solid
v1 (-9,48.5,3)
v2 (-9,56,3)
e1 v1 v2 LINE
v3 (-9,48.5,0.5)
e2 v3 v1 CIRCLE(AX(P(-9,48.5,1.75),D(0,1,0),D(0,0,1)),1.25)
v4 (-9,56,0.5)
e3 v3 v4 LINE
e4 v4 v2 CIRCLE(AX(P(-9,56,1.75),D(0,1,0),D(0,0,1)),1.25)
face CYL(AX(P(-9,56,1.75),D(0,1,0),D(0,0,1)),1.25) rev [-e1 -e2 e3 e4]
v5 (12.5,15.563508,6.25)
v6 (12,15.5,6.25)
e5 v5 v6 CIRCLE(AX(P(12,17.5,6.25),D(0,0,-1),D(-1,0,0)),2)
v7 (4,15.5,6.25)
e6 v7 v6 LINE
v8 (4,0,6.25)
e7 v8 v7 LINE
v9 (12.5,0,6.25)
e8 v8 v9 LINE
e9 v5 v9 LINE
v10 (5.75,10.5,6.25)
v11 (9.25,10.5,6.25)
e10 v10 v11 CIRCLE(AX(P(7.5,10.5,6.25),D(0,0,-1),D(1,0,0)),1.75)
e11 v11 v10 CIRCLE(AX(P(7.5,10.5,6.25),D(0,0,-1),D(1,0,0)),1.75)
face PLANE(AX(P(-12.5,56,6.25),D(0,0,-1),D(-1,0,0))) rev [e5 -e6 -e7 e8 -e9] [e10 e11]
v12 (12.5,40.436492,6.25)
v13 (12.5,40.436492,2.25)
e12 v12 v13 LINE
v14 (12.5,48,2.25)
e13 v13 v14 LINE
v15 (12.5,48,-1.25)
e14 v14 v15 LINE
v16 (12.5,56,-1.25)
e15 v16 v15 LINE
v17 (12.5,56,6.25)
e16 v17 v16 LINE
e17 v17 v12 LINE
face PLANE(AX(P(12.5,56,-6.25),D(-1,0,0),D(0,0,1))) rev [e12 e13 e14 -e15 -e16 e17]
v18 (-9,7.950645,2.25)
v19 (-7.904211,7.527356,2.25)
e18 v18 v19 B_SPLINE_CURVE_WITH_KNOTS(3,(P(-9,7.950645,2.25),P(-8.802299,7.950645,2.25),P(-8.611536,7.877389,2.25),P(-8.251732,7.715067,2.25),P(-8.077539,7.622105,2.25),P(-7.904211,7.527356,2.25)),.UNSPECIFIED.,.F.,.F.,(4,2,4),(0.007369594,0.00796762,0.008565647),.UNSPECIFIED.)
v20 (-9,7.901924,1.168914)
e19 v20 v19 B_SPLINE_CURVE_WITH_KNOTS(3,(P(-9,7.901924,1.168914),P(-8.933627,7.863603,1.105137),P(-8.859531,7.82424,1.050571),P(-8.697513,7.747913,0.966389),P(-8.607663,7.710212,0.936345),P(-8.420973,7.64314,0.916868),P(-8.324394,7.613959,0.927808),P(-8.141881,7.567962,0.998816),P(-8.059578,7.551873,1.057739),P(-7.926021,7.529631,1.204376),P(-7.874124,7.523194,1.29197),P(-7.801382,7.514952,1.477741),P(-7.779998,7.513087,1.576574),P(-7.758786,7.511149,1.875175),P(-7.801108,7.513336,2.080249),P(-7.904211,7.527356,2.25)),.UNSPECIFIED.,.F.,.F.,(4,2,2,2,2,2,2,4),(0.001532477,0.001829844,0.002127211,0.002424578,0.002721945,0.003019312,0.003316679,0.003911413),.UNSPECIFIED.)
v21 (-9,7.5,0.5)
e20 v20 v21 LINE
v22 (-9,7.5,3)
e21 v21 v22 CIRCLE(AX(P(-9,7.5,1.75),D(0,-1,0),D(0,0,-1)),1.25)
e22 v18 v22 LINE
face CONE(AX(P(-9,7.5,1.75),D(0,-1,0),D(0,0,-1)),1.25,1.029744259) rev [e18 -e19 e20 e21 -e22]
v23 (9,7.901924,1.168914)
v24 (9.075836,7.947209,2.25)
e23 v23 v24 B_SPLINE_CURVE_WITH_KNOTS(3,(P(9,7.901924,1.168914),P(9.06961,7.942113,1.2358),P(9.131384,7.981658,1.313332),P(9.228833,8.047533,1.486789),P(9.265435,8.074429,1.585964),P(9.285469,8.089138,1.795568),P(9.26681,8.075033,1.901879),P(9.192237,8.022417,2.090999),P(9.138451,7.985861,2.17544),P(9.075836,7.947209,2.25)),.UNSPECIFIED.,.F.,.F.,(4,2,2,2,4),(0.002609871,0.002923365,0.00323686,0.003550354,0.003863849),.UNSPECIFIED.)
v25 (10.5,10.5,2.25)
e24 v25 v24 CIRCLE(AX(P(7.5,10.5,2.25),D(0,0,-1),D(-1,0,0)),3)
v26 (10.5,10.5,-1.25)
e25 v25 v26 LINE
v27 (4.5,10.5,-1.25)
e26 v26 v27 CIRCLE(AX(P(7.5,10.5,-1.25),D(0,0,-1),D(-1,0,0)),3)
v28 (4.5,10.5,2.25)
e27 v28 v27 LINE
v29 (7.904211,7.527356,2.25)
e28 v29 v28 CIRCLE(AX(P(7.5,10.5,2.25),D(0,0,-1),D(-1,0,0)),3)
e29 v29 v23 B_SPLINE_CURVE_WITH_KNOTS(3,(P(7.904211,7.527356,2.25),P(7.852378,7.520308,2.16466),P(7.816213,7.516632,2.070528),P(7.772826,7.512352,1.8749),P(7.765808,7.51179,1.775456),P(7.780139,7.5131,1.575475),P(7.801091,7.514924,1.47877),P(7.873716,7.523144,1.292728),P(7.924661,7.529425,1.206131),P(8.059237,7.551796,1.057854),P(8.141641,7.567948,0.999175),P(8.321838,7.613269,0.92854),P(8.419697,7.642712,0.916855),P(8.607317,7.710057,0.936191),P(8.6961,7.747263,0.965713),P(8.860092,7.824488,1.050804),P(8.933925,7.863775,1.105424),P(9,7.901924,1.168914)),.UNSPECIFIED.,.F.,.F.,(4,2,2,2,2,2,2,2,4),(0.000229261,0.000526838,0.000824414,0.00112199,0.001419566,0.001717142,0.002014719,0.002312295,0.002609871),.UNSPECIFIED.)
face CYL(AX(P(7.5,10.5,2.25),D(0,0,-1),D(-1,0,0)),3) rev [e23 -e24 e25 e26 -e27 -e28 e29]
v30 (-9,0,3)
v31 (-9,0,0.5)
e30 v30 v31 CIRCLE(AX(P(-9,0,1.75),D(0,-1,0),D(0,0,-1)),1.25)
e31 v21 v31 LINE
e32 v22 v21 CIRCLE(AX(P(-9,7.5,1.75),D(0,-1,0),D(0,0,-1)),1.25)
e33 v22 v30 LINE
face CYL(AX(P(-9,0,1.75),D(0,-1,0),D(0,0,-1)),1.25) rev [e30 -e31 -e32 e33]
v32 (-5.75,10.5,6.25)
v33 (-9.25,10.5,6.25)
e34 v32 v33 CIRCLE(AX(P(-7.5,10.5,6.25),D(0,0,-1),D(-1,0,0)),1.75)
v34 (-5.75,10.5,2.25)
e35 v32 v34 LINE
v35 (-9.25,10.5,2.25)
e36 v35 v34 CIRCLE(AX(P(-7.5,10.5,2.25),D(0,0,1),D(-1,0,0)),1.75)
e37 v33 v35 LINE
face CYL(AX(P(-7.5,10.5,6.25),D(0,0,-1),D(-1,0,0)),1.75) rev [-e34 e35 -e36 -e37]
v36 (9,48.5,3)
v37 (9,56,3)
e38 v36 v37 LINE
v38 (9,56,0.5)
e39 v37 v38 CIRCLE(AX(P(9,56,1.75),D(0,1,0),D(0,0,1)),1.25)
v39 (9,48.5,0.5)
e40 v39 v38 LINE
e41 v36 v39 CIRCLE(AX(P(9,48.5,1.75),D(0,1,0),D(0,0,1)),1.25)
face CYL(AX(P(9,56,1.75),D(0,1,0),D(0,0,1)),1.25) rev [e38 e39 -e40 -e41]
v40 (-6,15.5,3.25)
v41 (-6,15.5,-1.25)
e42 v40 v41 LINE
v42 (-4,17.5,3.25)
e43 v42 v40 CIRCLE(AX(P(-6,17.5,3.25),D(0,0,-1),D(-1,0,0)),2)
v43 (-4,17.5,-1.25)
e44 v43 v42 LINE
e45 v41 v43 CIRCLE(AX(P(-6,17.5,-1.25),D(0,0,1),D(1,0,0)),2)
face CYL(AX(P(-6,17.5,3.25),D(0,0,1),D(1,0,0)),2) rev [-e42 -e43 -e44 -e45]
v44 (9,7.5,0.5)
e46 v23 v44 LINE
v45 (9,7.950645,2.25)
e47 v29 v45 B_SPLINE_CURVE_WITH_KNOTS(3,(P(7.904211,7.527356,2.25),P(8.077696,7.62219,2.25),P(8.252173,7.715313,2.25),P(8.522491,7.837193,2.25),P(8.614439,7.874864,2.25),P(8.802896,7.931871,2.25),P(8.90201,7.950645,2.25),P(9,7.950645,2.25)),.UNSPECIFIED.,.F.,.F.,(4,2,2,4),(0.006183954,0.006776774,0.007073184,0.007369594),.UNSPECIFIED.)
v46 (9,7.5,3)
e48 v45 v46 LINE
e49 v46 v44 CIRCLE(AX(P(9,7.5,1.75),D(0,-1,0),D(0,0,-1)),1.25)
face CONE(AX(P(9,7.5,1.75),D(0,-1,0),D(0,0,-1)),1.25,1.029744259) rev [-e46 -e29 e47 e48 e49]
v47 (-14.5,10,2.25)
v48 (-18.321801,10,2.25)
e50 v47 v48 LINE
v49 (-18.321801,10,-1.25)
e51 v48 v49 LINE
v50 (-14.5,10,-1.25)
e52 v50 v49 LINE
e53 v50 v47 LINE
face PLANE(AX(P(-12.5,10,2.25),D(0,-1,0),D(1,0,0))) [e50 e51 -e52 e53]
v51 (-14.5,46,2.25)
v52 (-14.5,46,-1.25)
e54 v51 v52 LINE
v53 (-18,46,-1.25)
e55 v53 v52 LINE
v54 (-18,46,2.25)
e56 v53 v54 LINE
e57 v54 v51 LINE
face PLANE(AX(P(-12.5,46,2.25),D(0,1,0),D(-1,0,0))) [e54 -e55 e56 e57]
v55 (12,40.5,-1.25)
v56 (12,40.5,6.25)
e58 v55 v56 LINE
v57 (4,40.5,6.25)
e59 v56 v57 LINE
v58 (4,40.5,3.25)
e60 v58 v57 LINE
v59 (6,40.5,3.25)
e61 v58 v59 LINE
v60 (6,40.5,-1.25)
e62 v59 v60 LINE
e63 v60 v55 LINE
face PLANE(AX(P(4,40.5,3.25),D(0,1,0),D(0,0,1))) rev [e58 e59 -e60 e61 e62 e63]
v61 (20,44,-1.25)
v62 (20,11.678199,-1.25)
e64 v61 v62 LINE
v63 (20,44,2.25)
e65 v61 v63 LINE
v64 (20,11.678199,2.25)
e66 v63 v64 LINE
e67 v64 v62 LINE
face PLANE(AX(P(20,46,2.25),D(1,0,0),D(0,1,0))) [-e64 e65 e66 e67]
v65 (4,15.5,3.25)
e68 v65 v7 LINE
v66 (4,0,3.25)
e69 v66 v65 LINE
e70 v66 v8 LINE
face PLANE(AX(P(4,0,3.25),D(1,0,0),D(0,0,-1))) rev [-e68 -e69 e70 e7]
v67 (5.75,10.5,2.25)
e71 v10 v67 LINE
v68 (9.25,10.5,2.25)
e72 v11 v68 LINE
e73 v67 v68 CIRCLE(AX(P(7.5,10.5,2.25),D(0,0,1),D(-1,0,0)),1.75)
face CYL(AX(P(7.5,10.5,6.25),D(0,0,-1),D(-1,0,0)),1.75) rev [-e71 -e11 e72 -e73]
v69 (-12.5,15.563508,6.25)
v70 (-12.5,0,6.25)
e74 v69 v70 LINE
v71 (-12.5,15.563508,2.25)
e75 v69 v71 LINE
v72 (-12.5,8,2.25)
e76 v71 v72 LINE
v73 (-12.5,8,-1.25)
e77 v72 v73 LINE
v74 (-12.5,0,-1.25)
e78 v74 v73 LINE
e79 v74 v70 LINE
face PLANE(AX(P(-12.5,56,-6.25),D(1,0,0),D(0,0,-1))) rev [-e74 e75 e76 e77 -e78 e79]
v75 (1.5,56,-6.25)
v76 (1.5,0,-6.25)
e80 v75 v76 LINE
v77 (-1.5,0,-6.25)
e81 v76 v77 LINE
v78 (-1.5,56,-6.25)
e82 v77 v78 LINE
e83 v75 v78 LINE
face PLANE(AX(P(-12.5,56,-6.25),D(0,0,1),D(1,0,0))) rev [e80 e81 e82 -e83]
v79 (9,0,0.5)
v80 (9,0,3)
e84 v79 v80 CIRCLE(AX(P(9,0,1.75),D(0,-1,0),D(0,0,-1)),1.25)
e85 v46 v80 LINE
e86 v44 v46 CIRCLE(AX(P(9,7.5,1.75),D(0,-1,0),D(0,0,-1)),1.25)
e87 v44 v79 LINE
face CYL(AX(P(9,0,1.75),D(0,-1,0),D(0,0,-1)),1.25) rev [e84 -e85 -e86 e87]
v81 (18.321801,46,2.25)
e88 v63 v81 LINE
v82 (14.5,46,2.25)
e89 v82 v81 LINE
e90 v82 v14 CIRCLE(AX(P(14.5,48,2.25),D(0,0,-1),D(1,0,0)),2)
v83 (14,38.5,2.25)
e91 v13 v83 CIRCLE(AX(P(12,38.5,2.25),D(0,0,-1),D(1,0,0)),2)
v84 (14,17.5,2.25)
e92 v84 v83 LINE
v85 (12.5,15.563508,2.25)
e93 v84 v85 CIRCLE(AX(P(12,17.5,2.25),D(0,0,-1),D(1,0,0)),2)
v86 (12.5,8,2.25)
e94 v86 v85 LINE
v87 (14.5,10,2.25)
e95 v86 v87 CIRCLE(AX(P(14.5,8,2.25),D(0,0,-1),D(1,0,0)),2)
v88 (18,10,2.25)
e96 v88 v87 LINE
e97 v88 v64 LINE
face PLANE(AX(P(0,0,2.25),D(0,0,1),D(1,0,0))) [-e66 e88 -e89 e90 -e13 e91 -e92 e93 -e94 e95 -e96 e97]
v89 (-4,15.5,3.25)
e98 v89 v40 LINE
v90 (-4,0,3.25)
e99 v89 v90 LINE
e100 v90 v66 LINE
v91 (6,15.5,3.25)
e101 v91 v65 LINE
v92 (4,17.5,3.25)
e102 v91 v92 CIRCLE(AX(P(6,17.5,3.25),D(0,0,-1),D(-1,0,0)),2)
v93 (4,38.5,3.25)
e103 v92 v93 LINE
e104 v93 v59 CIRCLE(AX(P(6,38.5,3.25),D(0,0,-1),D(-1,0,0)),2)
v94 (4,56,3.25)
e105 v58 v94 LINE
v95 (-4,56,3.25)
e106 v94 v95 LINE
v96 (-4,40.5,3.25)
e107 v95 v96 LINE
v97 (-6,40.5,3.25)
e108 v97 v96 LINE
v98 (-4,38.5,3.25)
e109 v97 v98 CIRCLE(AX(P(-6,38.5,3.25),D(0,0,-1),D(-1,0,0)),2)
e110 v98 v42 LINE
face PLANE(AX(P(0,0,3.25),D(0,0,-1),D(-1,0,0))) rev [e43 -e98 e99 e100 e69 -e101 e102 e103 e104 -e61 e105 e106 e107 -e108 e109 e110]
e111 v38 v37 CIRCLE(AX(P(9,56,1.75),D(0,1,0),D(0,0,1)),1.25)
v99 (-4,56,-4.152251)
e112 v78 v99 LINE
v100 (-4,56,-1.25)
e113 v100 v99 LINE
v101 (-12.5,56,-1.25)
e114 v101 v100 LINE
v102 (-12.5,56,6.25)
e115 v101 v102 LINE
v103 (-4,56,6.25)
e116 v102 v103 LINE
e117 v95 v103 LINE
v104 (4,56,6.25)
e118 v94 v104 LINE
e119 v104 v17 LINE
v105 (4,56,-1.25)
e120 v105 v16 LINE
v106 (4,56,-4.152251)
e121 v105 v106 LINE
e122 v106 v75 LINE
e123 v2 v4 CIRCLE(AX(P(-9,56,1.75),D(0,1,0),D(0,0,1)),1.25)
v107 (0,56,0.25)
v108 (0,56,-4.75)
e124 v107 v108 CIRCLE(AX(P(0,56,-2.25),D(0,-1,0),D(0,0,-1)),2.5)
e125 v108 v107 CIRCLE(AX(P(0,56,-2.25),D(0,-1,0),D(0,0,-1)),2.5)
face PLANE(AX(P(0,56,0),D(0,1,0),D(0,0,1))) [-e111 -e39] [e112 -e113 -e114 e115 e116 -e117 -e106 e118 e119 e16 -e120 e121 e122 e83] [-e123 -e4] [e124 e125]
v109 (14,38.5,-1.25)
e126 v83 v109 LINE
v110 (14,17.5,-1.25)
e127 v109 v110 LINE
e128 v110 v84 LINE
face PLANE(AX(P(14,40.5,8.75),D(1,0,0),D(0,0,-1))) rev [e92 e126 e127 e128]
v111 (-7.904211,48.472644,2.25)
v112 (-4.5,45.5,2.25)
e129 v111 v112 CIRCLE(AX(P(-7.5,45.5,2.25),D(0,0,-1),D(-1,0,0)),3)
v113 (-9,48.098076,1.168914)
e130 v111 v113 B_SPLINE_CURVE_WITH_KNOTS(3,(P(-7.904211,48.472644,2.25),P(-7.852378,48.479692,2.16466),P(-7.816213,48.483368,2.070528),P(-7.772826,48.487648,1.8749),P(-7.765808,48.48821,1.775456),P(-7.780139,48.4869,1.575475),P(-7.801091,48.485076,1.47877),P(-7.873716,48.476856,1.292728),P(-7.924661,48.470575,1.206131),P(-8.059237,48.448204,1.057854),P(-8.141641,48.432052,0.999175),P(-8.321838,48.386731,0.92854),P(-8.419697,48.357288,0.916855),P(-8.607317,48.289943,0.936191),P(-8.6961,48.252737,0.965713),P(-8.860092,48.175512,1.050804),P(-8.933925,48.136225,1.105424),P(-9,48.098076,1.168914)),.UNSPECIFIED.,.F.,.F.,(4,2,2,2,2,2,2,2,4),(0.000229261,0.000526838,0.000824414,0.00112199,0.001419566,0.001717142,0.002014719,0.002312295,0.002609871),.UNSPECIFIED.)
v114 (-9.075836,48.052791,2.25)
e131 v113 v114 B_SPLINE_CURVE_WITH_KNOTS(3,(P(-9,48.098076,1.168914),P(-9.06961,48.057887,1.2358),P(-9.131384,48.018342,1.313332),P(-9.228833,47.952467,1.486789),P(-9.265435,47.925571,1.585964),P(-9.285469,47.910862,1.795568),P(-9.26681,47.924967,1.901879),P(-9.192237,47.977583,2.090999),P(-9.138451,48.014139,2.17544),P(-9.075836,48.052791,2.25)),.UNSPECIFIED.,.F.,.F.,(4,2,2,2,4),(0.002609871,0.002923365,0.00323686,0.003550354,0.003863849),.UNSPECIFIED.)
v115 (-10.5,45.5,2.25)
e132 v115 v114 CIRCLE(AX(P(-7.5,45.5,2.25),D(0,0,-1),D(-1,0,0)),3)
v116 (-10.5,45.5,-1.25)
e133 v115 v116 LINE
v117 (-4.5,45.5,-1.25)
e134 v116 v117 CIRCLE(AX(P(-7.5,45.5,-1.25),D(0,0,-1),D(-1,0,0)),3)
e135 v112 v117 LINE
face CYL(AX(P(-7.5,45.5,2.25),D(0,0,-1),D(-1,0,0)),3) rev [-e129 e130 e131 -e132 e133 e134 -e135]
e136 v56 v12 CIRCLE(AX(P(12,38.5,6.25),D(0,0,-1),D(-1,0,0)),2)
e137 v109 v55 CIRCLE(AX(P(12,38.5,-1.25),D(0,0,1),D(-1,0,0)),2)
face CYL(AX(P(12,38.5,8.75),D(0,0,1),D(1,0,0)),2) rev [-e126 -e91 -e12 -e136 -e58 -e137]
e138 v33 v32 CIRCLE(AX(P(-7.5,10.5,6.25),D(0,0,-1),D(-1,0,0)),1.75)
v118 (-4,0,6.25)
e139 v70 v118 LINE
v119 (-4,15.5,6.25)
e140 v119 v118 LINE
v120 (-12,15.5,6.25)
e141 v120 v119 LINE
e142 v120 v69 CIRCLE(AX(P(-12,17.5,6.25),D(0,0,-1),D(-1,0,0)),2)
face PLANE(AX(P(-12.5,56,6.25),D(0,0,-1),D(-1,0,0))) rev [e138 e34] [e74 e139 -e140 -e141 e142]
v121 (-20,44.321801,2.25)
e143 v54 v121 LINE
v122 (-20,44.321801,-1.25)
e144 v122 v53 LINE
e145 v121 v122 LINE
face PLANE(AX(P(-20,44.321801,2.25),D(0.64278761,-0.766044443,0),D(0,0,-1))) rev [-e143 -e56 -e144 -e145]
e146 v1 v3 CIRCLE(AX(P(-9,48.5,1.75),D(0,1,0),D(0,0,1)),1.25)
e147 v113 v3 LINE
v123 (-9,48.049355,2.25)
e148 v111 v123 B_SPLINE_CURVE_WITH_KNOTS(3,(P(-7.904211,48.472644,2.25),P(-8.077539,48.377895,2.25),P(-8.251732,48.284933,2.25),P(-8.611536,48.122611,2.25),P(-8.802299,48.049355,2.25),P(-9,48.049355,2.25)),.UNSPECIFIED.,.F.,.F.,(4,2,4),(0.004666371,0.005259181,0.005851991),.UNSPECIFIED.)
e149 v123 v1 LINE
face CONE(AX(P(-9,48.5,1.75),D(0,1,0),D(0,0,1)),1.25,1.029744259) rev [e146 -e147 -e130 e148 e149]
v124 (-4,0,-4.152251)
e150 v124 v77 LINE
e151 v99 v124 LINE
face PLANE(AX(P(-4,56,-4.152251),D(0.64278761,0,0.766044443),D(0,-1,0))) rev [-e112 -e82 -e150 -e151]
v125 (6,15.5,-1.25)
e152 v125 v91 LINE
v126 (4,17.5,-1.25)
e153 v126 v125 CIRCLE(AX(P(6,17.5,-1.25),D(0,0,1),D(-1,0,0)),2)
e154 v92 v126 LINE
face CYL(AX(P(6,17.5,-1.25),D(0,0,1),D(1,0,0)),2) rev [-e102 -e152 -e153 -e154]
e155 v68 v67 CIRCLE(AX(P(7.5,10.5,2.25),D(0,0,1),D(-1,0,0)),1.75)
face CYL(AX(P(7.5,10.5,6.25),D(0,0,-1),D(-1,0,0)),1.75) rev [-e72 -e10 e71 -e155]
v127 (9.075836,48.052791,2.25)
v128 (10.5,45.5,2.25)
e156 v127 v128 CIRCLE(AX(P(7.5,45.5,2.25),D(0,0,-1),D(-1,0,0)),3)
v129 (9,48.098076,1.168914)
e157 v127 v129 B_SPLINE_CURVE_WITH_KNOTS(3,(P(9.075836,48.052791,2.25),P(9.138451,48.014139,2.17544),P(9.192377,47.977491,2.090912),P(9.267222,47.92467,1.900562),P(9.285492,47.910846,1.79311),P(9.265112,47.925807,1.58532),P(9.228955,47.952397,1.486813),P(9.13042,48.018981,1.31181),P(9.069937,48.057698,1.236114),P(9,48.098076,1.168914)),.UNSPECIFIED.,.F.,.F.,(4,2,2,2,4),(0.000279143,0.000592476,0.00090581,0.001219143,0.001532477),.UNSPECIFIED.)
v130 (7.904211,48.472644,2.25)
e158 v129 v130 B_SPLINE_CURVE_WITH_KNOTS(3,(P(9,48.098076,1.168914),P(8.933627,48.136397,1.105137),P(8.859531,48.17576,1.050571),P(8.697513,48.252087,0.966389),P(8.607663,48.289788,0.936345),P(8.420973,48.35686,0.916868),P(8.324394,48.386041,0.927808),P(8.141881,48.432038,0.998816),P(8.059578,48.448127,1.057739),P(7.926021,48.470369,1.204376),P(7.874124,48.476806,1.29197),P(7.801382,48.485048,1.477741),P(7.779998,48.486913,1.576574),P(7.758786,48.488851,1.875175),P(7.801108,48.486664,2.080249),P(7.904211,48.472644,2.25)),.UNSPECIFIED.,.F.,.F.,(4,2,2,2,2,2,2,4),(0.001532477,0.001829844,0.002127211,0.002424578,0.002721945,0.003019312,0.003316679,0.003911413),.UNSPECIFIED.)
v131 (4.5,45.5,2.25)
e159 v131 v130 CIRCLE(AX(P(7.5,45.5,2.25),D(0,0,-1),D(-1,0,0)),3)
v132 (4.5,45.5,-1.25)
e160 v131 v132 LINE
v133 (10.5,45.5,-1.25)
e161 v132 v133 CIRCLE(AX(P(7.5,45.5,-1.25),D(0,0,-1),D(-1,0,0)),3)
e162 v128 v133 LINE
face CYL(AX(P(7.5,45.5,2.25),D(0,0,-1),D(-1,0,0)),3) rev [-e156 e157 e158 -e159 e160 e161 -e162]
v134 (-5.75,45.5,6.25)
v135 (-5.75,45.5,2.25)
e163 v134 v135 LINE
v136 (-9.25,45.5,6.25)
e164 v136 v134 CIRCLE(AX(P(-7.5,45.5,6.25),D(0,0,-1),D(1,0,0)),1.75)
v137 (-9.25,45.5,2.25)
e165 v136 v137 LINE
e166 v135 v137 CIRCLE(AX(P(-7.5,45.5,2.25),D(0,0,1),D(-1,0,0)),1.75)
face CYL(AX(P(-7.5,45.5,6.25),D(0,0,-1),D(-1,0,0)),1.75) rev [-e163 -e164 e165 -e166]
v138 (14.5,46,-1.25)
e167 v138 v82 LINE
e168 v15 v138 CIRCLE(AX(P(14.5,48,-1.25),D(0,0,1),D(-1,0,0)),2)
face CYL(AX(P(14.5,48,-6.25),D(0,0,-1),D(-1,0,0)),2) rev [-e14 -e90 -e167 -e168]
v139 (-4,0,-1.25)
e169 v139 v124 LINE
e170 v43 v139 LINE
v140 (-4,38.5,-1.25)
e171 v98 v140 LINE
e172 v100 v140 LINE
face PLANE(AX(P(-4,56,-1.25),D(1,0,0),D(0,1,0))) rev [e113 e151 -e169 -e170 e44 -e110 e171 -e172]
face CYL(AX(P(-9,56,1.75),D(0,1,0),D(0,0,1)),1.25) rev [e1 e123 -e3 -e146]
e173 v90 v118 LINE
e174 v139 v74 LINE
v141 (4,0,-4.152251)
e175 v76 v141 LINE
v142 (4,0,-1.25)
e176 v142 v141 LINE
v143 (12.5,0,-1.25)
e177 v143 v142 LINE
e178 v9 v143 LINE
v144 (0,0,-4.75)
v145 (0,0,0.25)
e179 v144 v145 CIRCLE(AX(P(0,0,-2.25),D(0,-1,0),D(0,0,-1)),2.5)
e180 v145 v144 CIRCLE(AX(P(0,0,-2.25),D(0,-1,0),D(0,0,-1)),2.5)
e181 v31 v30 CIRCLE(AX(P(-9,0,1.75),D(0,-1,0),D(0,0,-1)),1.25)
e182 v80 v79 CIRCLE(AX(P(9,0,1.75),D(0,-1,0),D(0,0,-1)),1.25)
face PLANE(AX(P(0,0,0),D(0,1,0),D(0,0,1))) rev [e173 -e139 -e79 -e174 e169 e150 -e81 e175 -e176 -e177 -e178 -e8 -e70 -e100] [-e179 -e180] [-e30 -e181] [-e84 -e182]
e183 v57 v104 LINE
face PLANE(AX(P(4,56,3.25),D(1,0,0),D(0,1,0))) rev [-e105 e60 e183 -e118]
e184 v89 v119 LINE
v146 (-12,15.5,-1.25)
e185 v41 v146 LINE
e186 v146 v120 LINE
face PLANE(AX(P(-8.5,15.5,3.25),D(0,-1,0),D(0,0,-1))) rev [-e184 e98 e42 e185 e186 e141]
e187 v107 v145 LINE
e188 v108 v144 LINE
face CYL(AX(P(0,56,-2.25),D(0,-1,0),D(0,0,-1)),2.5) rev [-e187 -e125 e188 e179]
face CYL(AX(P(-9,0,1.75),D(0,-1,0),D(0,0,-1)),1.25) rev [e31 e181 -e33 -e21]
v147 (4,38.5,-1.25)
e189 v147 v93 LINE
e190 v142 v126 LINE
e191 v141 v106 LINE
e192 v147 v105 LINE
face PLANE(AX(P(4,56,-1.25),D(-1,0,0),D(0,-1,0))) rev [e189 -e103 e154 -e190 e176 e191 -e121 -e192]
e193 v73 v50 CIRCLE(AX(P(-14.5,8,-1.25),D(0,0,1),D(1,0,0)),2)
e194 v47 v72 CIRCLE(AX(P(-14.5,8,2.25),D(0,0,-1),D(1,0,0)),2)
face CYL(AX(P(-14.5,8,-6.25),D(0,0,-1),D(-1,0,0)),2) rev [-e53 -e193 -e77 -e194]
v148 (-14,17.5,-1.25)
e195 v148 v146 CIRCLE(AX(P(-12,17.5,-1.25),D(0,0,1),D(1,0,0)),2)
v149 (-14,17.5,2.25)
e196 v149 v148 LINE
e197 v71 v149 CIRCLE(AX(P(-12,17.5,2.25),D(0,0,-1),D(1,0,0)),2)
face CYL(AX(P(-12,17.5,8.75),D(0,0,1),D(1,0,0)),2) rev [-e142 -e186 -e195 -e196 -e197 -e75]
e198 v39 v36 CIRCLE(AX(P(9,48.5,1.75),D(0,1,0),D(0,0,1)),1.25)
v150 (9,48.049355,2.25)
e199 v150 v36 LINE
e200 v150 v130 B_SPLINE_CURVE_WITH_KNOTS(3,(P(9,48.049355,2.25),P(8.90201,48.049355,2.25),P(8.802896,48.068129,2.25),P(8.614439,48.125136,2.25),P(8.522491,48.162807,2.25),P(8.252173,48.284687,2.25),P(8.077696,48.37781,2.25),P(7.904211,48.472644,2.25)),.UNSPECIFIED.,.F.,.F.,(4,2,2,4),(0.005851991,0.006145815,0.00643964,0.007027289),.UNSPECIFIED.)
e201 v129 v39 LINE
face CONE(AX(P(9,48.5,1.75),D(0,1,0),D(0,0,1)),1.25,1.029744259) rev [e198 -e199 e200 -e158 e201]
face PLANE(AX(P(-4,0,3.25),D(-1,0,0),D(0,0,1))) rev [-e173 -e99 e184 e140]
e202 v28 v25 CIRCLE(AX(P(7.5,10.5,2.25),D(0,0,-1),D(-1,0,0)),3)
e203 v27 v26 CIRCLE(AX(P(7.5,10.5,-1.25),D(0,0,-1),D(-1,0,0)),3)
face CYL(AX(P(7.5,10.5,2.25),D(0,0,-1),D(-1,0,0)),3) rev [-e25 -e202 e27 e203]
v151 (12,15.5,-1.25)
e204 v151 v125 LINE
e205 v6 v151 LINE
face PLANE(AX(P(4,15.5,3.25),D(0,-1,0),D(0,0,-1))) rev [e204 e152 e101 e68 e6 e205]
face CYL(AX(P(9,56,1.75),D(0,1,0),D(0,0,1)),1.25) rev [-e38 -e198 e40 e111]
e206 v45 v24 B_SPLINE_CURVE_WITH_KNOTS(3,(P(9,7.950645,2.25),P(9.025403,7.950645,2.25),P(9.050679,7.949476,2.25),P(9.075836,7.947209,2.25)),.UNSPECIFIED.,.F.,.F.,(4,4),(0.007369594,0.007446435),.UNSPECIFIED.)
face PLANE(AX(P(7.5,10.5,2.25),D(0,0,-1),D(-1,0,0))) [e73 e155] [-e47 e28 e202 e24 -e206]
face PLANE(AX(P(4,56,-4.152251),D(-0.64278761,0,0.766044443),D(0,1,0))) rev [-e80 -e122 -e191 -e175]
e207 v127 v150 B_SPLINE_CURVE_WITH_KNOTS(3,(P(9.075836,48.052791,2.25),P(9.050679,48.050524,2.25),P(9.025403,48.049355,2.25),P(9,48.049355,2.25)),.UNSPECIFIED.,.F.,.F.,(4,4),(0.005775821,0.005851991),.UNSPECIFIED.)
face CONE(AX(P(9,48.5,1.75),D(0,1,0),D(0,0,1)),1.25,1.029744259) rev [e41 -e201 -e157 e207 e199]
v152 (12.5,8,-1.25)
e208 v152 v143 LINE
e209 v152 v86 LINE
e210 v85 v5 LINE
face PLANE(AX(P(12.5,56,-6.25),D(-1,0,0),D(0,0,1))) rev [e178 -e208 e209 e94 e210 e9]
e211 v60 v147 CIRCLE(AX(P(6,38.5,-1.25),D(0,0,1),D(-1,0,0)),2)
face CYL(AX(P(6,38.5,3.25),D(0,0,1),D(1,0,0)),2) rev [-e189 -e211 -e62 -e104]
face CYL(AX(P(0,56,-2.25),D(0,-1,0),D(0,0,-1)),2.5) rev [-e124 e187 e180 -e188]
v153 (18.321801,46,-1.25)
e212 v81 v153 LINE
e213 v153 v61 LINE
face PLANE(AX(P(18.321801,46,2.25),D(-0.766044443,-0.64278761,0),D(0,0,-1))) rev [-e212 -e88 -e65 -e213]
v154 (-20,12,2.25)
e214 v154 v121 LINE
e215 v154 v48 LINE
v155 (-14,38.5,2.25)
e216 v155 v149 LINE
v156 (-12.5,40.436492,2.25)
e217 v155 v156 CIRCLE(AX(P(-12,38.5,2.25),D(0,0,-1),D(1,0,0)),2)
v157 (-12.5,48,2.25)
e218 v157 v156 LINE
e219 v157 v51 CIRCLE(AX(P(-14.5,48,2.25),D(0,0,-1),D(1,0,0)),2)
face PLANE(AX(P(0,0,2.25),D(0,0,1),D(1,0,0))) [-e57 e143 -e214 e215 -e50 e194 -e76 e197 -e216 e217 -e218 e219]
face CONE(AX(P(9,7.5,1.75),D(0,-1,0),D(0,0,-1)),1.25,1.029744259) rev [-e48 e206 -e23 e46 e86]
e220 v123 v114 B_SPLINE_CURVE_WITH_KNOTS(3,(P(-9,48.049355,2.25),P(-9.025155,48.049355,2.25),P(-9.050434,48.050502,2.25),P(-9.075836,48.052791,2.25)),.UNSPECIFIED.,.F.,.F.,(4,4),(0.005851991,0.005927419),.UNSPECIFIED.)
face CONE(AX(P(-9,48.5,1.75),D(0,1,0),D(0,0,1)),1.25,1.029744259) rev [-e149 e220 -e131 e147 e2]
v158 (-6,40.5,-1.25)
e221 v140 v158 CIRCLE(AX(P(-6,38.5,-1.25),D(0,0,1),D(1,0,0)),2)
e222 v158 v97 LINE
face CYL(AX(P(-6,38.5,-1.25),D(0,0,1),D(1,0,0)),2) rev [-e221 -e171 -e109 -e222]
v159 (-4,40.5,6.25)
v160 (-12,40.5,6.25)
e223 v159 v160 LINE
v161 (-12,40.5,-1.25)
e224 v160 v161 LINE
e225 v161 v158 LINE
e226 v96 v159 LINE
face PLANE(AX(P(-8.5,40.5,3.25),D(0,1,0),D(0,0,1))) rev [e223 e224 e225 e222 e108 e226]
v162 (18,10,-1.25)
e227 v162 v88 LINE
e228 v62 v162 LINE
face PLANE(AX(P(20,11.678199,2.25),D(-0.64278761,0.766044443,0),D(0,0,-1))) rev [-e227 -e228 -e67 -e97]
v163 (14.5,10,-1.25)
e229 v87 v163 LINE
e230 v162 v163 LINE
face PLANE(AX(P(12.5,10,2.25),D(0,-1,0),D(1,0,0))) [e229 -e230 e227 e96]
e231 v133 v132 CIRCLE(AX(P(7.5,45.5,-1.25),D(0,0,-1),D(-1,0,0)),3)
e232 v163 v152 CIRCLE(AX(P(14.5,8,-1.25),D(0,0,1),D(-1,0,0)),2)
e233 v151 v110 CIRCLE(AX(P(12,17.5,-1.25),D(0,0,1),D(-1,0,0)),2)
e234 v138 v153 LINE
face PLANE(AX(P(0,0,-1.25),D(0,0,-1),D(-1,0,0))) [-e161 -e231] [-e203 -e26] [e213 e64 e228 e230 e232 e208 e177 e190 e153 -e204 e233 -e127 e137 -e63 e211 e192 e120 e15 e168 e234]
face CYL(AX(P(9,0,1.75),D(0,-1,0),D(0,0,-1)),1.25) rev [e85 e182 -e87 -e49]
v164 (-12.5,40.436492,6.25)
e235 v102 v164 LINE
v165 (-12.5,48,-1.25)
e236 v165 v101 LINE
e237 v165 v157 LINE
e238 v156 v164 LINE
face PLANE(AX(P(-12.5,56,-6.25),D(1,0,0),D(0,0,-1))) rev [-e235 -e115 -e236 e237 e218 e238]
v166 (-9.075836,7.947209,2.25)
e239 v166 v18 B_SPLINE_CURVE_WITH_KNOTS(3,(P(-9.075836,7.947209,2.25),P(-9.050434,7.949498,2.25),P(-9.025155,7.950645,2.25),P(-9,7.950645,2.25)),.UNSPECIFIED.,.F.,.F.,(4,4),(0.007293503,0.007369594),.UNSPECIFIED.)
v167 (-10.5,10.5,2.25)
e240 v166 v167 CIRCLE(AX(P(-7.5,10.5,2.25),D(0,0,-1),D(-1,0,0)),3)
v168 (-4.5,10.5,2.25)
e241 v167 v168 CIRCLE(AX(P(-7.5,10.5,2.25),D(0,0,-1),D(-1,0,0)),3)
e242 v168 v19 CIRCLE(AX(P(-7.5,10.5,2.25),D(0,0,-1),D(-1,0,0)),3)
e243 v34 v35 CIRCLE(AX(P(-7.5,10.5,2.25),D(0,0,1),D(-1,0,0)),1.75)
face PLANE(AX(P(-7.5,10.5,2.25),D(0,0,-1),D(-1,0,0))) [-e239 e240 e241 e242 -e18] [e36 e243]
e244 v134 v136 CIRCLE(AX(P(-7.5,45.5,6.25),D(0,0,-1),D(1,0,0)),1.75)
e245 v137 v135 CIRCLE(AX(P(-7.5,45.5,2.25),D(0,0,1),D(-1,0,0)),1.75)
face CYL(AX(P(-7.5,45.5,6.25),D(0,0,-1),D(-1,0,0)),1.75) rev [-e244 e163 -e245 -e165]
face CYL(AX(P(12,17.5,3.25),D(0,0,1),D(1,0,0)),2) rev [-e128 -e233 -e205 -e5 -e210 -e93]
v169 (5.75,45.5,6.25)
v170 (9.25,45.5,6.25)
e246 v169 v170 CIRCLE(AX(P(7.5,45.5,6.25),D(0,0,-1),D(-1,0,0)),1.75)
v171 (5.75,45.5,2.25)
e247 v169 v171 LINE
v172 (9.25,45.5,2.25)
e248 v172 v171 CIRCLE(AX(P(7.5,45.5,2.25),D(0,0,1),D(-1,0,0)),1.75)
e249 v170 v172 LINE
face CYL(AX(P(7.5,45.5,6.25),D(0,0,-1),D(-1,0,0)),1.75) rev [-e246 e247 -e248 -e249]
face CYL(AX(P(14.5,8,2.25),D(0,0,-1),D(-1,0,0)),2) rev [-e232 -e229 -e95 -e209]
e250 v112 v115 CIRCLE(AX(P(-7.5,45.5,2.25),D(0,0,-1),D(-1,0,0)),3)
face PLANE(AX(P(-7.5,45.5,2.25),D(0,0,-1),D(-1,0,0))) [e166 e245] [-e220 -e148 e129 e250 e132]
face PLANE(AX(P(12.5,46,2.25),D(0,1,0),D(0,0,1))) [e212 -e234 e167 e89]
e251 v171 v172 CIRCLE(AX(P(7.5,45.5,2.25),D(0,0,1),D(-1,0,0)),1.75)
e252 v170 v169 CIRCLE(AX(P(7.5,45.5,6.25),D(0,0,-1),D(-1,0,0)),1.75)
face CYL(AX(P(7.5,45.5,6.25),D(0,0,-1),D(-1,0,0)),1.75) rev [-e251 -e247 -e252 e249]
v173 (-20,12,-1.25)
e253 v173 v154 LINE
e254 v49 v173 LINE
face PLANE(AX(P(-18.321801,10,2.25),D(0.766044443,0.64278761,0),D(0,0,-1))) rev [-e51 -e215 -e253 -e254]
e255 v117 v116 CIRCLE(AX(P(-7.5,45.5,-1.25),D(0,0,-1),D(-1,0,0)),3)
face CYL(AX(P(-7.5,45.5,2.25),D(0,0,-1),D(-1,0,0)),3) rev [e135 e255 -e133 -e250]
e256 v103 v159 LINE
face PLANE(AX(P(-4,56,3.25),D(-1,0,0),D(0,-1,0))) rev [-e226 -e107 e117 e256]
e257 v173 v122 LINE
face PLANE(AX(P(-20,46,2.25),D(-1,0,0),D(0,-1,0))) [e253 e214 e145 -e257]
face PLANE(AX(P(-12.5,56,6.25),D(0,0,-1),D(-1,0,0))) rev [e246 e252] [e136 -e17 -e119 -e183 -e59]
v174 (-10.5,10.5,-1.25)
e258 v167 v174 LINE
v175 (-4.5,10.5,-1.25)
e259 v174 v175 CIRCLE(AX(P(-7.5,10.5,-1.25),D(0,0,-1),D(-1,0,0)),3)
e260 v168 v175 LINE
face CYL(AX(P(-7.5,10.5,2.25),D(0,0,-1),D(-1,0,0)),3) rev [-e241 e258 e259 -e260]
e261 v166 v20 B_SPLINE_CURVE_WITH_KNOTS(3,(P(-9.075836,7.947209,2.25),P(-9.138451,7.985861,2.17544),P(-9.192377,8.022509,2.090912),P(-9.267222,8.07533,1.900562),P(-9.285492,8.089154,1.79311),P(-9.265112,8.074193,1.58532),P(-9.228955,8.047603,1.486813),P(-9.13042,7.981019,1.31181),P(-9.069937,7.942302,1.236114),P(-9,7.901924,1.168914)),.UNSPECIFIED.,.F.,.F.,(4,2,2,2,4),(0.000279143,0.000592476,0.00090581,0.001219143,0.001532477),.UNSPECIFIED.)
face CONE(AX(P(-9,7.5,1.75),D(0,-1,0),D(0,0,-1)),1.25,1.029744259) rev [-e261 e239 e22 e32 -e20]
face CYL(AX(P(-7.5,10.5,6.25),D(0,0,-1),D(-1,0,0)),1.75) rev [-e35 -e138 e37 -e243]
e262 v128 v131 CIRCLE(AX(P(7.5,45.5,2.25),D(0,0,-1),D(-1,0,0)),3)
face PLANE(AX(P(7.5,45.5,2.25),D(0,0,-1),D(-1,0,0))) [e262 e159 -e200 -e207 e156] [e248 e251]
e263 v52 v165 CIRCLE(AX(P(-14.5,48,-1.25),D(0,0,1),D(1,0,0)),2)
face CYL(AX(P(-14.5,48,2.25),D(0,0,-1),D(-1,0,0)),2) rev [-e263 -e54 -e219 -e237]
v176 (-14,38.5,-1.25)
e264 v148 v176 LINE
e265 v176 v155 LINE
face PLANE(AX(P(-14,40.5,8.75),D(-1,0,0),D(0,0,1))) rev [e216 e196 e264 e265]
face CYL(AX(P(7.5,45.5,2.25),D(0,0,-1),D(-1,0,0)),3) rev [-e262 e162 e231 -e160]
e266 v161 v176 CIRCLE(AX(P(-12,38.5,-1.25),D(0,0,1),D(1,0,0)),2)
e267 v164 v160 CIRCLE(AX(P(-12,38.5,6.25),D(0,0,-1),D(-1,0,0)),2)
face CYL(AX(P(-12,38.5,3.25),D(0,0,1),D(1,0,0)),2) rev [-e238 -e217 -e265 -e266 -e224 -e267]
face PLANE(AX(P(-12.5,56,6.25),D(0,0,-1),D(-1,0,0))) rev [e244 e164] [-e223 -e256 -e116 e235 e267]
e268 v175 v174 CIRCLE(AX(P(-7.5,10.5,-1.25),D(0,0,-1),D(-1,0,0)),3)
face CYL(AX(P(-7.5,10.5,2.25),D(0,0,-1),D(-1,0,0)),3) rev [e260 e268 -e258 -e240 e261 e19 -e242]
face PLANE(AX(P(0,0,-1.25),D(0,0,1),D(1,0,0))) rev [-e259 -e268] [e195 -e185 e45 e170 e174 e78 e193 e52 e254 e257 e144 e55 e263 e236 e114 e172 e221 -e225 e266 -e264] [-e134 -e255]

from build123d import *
from OCP.BRepFilletAPI import BRepFilletAPI_MakeChamfer

# Parameters (mm, degrees)
SKETCH1_W             = 25
SKETCH1_H             = 12.5
BOSS_EXTRUDE1_DEPTH   = 56
SKETCH3_W             = 8.5
SKETCH3_H             = 56
CUT_EXTRUDE2_DEPTH    = 5
SKETCH4_R             = 2.5
CUT_EXTRUDE3_DEPTH    = 58.717523336
SKETCH5_R             = 1.75
CUT_EXTRUDE4_DEPTH    = 58.866225037
SKETCH6_R             = 3
CUT_EXTRUDE5_DEPTH    = 3.5
CHAMFER1_SIZE         = 2.5
CHAMFER1_SIZE2        = 2.097749078
SKETCH8_W             = 7.5
SKETCH8_H             = 36
BOSS_EXTRUDE3_DEPTH   = 3.5
M3_TAPPED_HOLE1_D     = 2.5
M3_TAPPED_HOLE1_DEPTH = 7.5
M3_TAPPED_HOLE1_TIP   = 0.751075774
M3_TAPPED_HOLE2_D     = 2.5
M3_TAPPED_HOLE2_DEPTH = 7.5
M3_TAPPED_HOLE2_TIP   = 0.751075774
CHAMFER2_SIZE         = 2
CHAMFER2_SIZE2        = 1.678199262
FILLET1_R             = 2
CUT_EXTRUDE7_DEPTH    = 3
SKETCH17_W            = 10
SKETCH17_H            = 25
CUT_EXTRUDE8_DEPTH    = 10
FILLET3_R             = 2


with BuildPart() as part:
    # Sketch1 → Boss-Extrude1 (new body)
    with BuildSketch(Plane(origin=(0, 0, 0), x_dir=(1, 0, 0), z_dir=(0, 1, 0))):
        Rectangle(SKETCH1_W, SKETCH1_H)
    extrude(amount=BOSS_EXTRUDE1_DEPTH)

    # Sketch3 → Cut-Extrude2 (cut)
    with BuildSketch(Plane(origin=(0, 0, -6.25), x_dir=(-1, 0, 0), z_dir=(0, 0, -1))):
        with Locations((-8.25, 28)):
            Rectangle(SKETCH3_W, SKETCH3_H)
        with Locations((8.25, 28)):
            Rectangle(SKETCH3_W, SKETCH3_H)
    extrude(amount=-CUT_EXTRUDE2_DEPTH, mode=Mode.SUBTRACT)

    # Sketch4 → Cut-Extrude3 (cut, through all)
    with BuildSketch(Plane.XZ):
        with Locations(Location((0, -2.25, 0), (0, 0, 270))):
            Circle(SKETCH4_R)
    extrude(amount=-CUT_EXTRUDE3_DEPTH, mode=Mode.SUBTRACT)

    # Sketch5 → Cut-Extrude4 (cut, through all)
    with BuildSketch(Plane(origin=(0, 0, -1.25), x_dir=(-1, 0, 0), z_dir=(0, 0, -1))):
        with Locations((-7.5, 45.5)):
            Circle(SKETCH5_R)
        with Locations((7.5, 45.5)):
            Circle(SKETCH5_R)
        with Locations((7.5, 10.5)):
            Circle(SKETCH5_R)
        with Locations((-7.5, 10.5)):
            Circle(SKETCH5_R)
    extrude(amount=-CUT_EXTRUDE4_DEPTH, mode=Mode.SUBTRACT)

    # Sketch6 → Cut-Extrude5 (cut)
    with BuildSketch(Plane(origin=(0, 0, -1.25), x_dir=(-1, 0, 0), z_dir=(0, 0, -1))):
        with Locations((-7.5, 45.5)):
            Circle(SKETCH6_R)
        with Locations((7.5, 45.5)):
            Circle(SKETCH6_R)
        with Locations((7.5, 10.5)):
            Circle(SKETCH6_R)
        with Locations((-7.5, 10.5)):
            Circle(SKETCH6_R)
    extrude(amount=-CUT_EXTRUDE5_DEPTH, mode=Mode.SUBTRACT)

    # Chamfer1
    chamfer1_edges = [part.edges().sort_by_distance(p)[0] for p in [
        (4, 28, -6.25),
        (-4, 28, -6.25),
    ]]
    chamfer1_side = [part.faces().sort_by_distance(p)[0] for p in [
        (0, 28, -6.25),
    ]]
    chamfer(chamfer1_edges, length=CHAMFER1_SIZE, length2=CHAMFER1_SIZE2, reference=chamfer1_side[0])

    # Sketch8 → Boss-Extrude3 (add)
    with BuildSketch(Plane(origin=(0, 0, -1.25), x_dir=(-1, 0, 0), z_dir=(0, 0, -1))):
        with Locations((-16.25, 28)):
            Rectangle(SKETCH8_W, SKETCH8_H)
        with Locations((16.25, 28)):
            Rectangle(SKETCH8_W, SKETCH8_H)
    extrude(amount=-BOSS_EXTRUDE3_DEPTH)

    # M3 Tapped Hole1
    with Locations(Plane(origin=(0, 0, 0), x_dir=(-1, 0, 0), z_dir=(0, -1, 0))):
        with Locations((-9, -1.75), (9, -1.75)):
            Hole(M3_TAPPED_HOLE1_D / 2, depth=M3_TAPPED_HOLE1_DEPTH)
            with Locations((0, 0, -(M3_TAPPED_HOLE1_DEPTH + M3_TAPPED_HOLE1_TIP / 2))):  # 118° drill point
                Cone(0, M3_TAPPED_HOLE1_D / 2, M3_TAPPED_HOLE1_TIP, mode=Mode.SUBTRACT)

    # M3 Tapped Hole2
    with Locations(Plane(origin=(0, 56, 0), x_dir=(1, 0, 0), z_dir=(0, 1, 0))):
        with Locations((-9, -1.75), (9, -1.75)):
            Hole(M3_TAPPED_HOLE2_D / 2, depth=M3_TAPPED_HOLE2_DEPTH)
            with Locations((0, 0, -(M3_TAPPED_HOLE2_DEPTH + M3_TAPPED_HOLE2_TIP / 2))):  # 118° drill point
                Cone(0, M3_TAPPED_HOLE2_D / 2, M3_TAPPED_HOLE2_TIP, mode=Mode.SUBTRACT)

    # Chamfer2: one chamfer whose edges measure the first distance from different faces: ONE call of the kernel's chamfer builder (chamfer() names one face for all edges)
    chamfer2_edges_1 = [part.edges().sort_by_distance(p)[0] for p in [
        (-20, 46, 0.5),
    ]]
    chamfer2_side_1 = [part.faces().sort_by_distance(p)[0] for p in [
        (-16.25, 46, 0.5),
    ]]
    chamfer2_edges_2 = [part.edges().sort_by_distance(p)[0] for p in [
        (20, 46, 0.5),
    ]]
    chamfer2_side_2 = [part.faces().sort_by_distance(p)[0] for p in [
        (20, 28, 0.5),
    ]]
    chamfer2_edges_3 = [part.edges().sort_by_distance(p)[0] for p in [
        (20, 10, 0.5),
    ]]
    chamfer2_side_3 = [part.faces().sort_by_distance(p)[0] for p in [
        (16.25, 10, 0.5),
    ]]
    chamfer2_edges_4 = [part.edges().sort_by_distance(p)[0] for p in [
        (-20, 10, 0.5),
    ]]
    chamfer2_side_4 = [part.faces().sort_by_distance(p)[0] for p in [
        (-20, 28, 0.5),
    ]]
    chamfer2 = BRepFilletAPI_MakeChamfer(part.part.solid().wrapped)
    for e in chamfer2_edges_1:
        chamfer2.Add(CHAMFER2_SIZE, CHAMFER2_SIZE2, e.wrapped, chamfer2_side_1[0].wrapped)  # the first distance lies on this face
    for e in chamfer2_edges_2:
        chamfer2.Add(CHAMFER2_SIZE, CHAMFER2_SIZE2, e.wrapped, chamfer2_side_2[0].wrapped)  # the first distance lies on this face
    for e in chamfer2_edges_3:
        chamfer2.Add(CHAMFER2_SIZE, CHAMFER2_SIZE2, e.wrapped, chamfer2_side_3[0].wrapped)  # the first distance lies on this face
    for e in chamfer2_edges_4:
        chamfer2.Add(CHAMFER2_SIZE, CHAMFER2_SIZE2, e.wrapped, chamfer2_side_4[0].wrapped)  # the first distance lies on this face
    add(Compound.cast(chamfer2.Shape()), mode=Mode.REPLACE)

    # Fillet1
    fillet1_edges = [part.edges().sort_by_distance(p)[0] for p in [
        (-12.5, 46, 0.5),
        (12.5, 46, 0.5),
        (12.5, 10, 0.5),
        (-12.5, 10, 0.5),
    ]]
    fillet(fillet1_edges, radius=FILLET1_R)

    # Sketch16 → Cut-Extrude7 (cut)
    with BuildSketch(Plane.XY.offset(6.25)):
        Polygon((4, 40.5), (8.5, 40.5), (8.5, 15.5), (4, 15.5), (4, 0), (-4, 0), (-4, 15.5), (-8.5, 15.5), (-8.5, 40.5), (-4, 40.5), (-4, 56), (4, 56), align=None)
    extrude(amount=-CUT_EXTRUDE7_DEPTH, mode=Mode.SUBTRACT)

    # Sketch17 → Cut-Extrude8 (cut)
    with BuildSketch(Plane(origin=(0, 0, -1.25), x_dir=(-1, 0, 0), z_dir=(0, 0, -1))):
        with Locations((-9, 28)):
            Rectangle(SKETCH17_W, SKETCH17_H)
        with Locations((9, 28)):
            Rectangle(SKETCH17_W, SKETCH17_H)
    extrude(amount=-CUT_EXTRUDE8_DEPTH, mode=Mode.SUBTRACT)

    # Fillet3
    fillet3_edges = [part.edges().sort_by_distance(p)[0] for p in [
        (-4, 15.5, 1),
        (4, 15.5, 1),
        (4, 40.5, 1),
        (-14, 40.5, 0.5),
        (-14, 15.5, 0.5),
        (14, 15.5, 0.5),
        (14, 40.5, 0.5),
        (-4, 40.5, 1),
    ]]
    fillet(fillet3_edges, radius=FILLET3_R)


solid = part.part
